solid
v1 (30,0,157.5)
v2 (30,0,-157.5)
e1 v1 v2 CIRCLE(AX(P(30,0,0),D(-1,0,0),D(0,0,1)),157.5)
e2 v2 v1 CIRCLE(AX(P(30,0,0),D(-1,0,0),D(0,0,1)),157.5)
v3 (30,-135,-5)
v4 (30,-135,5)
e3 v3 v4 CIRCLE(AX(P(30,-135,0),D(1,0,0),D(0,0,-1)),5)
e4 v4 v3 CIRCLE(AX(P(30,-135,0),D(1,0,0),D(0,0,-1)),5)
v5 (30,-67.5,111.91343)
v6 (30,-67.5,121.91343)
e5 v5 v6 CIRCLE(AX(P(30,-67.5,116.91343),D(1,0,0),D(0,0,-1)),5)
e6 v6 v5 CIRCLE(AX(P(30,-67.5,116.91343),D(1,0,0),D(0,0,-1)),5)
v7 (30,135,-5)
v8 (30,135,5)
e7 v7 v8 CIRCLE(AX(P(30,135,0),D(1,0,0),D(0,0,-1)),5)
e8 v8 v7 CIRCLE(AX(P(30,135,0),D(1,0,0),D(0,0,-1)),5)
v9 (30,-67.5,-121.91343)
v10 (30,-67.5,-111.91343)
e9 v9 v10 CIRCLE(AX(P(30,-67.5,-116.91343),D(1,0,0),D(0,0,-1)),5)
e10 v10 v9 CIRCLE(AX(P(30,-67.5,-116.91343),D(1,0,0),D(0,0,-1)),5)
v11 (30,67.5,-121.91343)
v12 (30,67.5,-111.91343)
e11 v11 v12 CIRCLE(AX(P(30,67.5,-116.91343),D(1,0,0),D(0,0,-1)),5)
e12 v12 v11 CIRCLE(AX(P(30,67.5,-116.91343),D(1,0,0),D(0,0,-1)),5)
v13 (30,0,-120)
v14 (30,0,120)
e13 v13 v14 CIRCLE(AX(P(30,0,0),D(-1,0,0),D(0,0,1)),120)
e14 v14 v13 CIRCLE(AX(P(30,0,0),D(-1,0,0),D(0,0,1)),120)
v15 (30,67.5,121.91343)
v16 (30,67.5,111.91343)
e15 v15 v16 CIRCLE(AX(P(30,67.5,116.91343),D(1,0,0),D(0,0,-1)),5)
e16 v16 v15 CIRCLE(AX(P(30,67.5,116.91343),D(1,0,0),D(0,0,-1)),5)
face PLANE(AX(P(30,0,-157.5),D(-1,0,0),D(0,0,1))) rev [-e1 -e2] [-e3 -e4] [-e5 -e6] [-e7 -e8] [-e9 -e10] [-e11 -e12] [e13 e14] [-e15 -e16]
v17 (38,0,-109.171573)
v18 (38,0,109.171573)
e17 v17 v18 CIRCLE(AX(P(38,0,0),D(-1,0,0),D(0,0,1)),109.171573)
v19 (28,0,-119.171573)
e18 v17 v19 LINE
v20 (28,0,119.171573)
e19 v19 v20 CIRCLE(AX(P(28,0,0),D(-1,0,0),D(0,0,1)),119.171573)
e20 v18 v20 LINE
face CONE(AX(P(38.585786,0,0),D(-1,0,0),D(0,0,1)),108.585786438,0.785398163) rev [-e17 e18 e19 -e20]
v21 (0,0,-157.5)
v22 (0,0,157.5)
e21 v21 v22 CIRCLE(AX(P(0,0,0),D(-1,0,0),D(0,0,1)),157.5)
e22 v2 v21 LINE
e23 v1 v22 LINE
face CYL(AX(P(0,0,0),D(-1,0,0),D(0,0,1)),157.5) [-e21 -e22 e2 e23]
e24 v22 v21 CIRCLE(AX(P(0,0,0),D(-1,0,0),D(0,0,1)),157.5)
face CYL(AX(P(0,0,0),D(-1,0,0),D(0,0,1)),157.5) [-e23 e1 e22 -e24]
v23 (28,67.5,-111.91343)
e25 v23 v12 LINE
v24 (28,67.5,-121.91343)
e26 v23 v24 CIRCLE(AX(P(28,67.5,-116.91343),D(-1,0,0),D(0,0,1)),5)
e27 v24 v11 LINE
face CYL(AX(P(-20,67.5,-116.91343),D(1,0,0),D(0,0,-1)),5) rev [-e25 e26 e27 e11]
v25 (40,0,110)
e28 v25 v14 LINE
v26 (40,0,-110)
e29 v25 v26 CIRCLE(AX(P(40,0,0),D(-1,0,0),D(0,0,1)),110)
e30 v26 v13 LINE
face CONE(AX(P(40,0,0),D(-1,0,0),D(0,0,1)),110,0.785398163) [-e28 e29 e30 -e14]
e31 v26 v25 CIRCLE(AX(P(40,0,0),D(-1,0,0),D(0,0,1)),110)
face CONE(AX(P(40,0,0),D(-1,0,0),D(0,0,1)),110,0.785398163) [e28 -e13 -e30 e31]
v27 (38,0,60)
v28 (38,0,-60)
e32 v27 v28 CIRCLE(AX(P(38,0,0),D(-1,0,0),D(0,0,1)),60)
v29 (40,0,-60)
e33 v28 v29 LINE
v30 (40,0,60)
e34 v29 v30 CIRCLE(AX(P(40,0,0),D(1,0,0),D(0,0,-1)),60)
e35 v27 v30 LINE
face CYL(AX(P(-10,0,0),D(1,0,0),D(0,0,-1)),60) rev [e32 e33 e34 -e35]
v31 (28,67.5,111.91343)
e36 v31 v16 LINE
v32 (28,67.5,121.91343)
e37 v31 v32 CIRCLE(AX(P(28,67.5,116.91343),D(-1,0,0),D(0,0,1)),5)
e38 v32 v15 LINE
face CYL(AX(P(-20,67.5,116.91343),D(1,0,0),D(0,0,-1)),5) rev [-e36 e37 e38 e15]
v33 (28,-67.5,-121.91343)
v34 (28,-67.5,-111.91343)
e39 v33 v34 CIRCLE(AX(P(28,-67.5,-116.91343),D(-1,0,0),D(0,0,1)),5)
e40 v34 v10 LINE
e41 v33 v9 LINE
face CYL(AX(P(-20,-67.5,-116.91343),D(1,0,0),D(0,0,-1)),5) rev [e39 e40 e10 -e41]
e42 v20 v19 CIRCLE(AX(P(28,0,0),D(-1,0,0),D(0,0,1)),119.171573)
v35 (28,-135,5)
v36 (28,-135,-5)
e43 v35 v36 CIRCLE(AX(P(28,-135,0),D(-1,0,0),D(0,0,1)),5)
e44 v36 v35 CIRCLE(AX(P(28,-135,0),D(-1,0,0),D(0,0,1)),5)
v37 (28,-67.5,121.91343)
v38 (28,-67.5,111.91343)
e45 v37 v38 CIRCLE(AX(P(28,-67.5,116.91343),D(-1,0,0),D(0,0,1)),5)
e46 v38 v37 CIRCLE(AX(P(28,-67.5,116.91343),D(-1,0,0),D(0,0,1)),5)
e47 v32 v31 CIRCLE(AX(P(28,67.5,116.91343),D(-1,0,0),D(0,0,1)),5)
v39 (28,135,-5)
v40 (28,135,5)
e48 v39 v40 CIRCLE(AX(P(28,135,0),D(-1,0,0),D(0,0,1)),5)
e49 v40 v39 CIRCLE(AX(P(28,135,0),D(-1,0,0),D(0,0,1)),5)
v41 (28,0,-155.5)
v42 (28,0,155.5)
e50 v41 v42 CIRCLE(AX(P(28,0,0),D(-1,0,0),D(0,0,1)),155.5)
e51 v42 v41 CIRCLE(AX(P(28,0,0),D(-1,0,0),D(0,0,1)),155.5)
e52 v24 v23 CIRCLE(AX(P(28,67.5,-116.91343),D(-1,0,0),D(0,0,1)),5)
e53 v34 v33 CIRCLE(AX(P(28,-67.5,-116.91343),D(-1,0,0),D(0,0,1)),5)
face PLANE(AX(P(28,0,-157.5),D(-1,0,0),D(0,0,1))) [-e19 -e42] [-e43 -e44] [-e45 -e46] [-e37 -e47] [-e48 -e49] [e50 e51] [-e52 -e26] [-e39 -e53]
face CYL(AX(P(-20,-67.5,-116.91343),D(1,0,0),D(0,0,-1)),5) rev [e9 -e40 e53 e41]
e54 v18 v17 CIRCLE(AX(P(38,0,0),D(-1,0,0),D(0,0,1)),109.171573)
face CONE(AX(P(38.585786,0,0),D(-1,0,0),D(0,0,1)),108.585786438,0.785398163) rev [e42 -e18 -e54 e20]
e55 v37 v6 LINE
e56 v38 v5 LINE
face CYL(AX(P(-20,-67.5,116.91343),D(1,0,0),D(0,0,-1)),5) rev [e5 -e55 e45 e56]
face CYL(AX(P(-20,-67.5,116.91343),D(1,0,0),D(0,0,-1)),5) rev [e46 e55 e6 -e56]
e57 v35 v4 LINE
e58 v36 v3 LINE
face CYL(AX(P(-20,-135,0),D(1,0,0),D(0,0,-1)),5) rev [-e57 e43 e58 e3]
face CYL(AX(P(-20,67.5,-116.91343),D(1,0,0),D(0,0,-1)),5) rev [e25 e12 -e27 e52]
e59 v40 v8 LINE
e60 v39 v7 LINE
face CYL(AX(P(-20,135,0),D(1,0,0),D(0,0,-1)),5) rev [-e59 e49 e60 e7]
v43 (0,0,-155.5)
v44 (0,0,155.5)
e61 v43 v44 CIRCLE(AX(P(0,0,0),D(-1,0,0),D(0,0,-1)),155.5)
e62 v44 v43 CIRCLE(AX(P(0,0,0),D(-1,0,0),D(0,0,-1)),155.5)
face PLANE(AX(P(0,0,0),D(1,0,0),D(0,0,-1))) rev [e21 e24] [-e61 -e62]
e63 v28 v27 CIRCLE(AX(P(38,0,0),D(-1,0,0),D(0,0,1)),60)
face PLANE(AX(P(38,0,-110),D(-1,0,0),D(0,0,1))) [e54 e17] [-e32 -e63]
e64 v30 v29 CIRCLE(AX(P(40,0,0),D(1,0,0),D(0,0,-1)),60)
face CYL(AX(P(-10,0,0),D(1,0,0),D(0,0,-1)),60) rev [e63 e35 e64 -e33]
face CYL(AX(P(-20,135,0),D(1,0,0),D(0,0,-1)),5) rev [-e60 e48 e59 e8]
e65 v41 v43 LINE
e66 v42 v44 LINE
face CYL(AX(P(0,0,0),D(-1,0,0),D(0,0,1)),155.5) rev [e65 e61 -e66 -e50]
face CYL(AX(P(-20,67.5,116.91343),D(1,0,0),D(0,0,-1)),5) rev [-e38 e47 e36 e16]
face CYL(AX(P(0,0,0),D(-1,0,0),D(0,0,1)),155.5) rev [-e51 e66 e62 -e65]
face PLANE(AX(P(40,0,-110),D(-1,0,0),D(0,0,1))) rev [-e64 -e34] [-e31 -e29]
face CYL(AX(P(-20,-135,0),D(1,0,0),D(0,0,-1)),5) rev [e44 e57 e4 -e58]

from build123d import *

# Parameters (mm, degrees)
SHELL1_T           = -2
SKETCH2_R          = 60
CUT_EXTRUDE1_DEPTH = 50
SKETCH3_R          = 5
CUT_EXTRUDE2_DEPTH = 50


with BuildPart() as part:
    # Sketch1 → Revolve1 (revolve)
    with BuildSketch(Plane(origin=(0, 0, 0), x_dir=(1, 0, 0), z_dir=(0, 1, 0)), mode=Mode.PRIVATE) as revolve1_sk:
        Polygon((0, 0), (0, 157.5), (30, 157.5), (30, 120), (40, 110), (40, 0), align=None)
    revolve(revolve1_sk.sketch.rotate(Axis((0, 0, 0), (1, 0, 0)), 180), axis=Axis((0, 0, 0), (1, 0, 0)))

    # Shell1
    shell1_openings = [part.faces().sort_by_distance(p)[0] for p in [
        (0, 0, 0),
    ]]
    offset(amount=SHELL1_T, openings=shell1_openings, kind=Kind.INTERSECTION)

    # Sketch2 → Cut-Extrude1 (cut)
    with BuildSketch(Plane(origin=(40, 0, 0), x_dir=(0, 0, -1), z_dir=(1, 0, 0))):
        Circle(SKETCH2_R)
    extrude(amount=-CUT_EXTRUDE1_DEPTH, mode=Mode.SUBTRACT)

    # Sketch3 → Cut-Extrude2 (cut)
    with BuildSketch(Plane(origin=(30, 0, 0), x_dir=(0, 0, -1), z_dir=(1, 0, 0))):
        with Locations((0, 135)):
            Circle(SKETCH3_R)
        with Locations((116.913429511, 67.5)):
            Circle(SKETCH3_R)
        with Locations((116.913429511, -67.5)):
            Circle(SKETCH3_R)
        with Locations((0, -135)):
            Circle(SKETCH3_R)
        with Locations((-116.913429511, -67.5)):
            Circle(SKETCH3_R)
        with Locations((-116.913429511, 67.5)):
            Circle(SKETCH3_R)
    extrude(amount=-CUT_EXTRUDE2_DEPTH, mode=Mode.SUBTRACT)


solid = part.part
